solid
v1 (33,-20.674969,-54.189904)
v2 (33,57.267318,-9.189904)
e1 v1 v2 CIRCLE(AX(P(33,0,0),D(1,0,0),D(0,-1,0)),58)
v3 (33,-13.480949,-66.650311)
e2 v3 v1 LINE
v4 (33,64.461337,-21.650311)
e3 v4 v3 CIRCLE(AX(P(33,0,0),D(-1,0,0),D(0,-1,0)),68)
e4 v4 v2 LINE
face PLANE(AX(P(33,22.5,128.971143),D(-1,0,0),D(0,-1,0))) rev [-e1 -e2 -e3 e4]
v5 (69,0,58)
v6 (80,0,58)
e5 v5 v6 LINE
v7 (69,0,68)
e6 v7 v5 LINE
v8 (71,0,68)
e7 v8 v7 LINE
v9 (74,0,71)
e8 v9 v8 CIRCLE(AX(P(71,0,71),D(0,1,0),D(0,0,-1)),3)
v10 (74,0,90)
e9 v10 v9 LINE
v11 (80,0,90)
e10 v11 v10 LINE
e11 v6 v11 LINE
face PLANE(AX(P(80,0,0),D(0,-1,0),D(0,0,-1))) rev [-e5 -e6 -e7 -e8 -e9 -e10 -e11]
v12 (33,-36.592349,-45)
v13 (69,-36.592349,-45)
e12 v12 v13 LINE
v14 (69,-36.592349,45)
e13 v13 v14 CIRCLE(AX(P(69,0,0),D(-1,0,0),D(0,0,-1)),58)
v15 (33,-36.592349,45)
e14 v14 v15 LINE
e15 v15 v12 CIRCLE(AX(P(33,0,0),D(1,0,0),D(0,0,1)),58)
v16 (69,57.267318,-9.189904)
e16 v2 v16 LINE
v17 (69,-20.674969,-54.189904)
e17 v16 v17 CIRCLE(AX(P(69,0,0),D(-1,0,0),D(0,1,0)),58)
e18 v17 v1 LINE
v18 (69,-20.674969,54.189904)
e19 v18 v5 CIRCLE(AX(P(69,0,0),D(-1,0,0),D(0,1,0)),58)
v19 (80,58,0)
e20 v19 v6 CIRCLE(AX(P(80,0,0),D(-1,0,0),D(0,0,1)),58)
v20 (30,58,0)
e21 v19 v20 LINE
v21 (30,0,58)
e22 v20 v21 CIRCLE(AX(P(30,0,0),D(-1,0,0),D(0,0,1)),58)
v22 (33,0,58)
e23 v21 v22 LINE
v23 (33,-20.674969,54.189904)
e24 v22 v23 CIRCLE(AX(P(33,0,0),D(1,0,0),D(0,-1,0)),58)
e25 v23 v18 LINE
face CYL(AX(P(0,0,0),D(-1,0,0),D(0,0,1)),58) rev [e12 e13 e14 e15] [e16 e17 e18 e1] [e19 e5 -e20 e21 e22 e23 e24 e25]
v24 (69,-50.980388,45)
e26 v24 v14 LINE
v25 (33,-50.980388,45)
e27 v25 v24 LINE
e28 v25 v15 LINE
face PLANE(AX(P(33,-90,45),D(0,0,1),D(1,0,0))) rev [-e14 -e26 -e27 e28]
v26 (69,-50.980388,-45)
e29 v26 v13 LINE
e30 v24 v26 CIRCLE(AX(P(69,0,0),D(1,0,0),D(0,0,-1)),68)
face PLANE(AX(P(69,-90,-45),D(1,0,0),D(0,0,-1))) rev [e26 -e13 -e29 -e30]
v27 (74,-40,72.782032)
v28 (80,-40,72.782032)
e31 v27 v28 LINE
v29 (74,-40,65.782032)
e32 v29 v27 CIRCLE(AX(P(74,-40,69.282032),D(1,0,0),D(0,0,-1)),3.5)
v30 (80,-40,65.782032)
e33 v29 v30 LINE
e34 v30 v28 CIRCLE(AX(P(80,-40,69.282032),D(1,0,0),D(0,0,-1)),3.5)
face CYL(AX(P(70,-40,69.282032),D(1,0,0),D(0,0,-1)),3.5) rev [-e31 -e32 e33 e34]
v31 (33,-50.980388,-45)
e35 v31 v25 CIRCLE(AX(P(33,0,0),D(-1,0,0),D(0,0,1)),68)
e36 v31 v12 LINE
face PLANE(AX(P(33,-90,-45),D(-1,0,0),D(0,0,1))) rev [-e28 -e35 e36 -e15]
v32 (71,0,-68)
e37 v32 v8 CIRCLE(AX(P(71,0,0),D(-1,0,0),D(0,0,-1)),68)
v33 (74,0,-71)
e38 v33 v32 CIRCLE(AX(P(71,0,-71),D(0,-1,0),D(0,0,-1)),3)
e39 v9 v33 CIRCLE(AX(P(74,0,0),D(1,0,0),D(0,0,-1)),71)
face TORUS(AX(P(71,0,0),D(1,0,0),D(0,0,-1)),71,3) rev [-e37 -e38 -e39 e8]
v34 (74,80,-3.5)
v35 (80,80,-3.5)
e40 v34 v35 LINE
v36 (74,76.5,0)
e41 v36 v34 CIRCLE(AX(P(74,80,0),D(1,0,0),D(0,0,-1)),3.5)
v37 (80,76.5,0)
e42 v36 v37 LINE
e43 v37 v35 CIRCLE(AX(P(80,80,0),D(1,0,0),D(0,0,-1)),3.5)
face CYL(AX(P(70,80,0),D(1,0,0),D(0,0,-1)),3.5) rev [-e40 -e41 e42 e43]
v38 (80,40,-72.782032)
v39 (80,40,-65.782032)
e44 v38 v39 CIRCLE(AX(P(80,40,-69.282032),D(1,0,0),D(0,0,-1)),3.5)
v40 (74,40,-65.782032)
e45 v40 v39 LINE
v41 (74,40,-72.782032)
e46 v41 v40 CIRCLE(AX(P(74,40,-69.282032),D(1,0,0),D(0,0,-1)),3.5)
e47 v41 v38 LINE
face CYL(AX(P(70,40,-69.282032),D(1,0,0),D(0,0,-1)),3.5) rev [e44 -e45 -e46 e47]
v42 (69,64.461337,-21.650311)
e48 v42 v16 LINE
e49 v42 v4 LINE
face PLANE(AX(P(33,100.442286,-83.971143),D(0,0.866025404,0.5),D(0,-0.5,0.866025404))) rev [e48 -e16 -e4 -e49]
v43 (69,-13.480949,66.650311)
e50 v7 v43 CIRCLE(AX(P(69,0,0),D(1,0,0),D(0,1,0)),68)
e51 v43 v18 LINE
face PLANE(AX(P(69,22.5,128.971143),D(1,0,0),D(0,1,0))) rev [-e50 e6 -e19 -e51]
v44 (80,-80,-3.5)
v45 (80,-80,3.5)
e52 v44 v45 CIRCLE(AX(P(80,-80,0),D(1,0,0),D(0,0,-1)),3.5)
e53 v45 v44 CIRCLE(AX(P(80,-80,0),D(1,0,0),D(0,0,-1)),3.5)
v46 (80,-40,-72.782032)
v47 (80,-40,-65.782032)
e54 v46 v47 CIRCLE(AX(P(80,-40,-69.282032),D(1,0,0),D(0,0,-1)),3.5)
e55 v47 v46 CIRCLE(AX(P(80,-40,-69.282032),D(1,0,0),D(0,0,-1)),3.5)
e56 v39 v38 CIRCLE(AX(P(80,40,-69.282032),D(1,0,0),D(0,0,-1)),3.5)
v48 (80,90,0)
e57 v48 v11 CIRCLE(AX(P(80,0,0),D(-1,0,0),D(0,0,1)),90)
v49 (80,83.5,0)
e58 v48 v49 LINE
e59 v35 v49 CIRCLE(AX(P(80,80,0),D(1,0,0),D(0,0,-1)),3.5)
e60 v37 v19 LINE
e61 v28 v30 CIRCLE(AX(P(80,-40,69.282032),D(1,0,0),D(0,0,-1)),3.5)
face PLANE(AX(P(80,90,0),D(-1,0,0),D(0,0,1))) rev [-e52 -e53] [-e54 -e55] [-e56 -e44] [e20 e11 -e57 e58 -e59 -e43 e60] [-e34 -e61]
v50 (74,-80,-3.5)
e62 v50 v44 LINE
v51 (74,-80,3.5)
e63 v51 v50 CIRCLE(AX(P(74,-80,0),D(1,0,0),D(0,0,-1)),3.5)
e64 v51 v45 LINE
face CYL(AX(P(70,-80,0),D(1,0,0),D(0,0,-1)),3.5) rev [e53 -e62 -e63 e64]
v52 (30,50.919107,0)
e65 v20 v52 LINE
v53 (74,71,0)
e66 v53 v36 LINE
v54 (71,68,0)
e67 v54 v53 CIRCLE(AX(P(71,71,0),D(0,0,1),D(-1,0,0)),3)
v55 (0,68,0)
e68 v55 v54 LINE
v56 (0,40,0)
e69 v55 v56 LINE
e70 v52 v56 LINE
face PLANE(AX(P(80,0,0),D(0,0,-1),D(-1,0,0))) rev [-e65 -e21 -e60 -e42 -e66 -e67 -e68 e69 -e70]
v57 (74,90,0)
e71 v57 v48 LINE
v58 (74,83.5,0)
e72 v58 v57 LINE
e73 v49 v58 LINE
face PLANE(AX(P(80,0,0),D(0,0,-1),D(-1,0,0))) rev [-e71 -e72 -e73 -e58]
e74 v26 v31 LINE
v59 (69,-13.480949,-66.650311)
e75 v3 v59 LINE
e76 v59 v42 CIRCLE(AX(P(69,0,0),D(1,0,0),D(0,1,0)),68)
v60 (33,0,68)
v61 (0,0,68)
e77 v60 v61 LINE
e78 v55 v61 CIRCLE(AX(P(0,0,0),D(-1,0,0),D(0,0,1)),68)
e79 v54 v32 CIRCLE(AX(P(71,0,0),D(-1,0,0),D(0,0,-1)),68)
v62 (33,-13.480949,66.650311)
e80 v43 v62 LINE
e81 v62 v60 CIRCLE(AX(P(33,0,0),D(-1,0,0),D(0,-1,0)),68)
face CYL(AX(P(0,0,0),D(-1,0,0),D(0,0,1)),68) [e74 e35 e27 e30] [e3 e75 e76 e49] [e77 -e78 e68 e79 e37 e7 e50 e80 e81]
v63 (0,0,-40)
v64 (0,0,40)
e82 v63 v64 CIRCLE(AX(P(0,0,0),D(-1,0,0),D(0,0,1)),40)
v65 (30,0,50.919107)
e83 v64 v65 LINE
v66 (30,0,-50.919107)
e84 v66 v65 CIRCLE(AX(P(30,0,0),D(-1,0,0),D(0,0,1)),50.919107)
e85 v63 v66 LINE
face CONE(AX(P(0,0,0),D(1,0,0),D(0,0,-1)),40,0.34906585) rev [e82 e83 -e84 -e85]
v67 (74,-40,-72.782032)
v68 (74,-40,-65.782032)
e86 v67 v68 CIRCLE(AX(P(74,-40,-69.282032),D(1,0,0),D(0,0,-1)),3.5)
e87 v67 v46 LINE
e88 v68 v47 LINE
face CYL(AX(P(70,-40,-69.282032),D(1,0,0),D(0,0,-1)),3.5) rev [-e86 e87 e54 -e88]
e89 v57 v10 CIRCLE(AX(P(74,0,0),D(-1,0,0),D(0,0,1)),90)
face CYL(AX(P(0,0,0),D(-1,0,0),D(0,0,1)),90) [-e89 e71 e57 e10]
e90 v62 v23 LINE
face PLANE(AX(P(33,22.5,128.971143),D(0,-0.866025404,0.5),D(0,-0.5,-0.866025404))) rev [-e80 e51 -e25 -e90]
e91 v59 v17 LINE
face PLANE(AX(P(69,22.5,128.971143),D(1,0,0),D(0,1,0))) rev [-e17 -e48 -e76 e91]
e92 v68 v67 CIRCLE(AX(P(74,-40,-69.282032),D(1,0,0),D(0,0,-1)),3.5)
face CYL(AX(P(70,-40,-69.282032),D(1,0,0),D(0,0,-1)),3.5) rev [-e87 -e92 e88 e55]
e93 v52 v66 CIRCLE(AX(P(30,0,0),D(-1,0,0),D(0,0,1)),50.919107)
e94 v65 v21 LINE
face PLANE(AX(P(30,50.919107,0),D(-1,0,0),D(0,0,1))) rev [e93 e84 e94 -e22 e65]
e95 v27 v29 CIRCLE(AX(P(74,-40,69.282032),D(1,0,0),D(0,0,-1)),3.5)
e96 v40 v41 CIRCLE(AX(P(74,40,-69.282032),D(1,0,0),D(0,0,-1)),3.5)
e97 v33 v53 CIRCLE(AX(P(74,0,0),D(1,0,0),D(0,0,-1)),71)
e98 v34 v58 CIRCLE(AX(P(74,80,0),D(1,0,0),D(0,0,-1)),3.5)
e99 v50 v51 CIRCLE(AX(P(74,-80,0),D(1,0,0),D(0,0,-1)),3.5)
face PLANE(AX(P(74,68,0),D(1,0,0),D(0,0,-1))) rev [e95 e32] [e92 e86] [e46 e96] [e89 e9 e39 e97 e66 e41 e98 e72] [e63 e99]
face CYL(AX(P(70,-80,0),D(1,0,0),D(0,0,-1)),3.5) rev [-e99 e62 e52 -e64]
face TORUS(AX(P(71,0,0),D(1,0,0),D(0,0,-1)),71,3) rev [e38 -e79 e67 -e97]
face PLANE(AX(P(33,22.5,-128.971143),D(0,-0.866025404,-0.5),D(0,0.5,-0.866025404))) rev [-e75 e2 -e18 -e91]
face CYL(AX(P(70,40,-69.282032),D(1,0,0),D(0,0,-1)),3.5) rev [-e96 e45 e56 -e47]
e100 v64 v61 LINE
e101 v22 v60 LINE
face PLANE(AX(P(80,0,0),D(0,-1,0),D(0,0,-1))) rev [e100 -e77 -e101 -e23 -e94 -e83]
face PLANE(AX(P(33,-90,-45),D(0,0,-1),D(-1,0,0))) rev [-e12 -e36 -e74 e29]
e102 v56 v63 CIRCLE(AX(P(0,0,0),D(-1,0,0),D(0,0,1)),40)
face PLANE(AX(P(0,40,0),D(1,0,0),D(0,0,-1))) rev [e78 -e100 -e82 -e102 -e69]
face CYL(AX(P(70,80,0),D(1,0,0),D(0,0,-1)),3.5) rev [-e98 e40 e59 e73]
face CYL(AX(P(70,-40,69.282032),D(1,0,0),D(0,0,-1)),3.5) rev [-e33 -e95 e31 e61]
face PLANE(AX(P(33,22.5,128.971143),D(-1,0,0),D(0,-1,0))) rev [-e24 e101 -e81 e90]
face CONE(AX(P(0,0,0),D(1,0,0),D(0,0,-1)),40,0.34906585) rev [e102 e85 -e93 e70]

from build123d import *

# Parameters (mm, degrees)
SKETCH2_R          = 3.5
CUT_EXTRUDE1_DEPTH = 10
FILLET1_R          = 3
SKETCH3_W          = 36
SKETCH3_H          = 90
CUT_EXTRUDE2_DEPTH = 151.332963784
CIRPATTERN1_COUNT  = 3
SKETCH4_W          = 114.578796514
SKETCH4_H          = 147.158368746
CUT_EXTRUDE3_DEPTH = 151.332963784


with BuildPart() as part:
    # Sketch1 → Revolve1 (revolve)
    with BuildSketch(Plane.XY, mode=Mode.PRIVATE) as revolve1_sk:
        Polygon((0, 40), (0, 68), (74, 68), (74, 90), (80, 90), (80, 58), (30, 58), (30, 50.919107028), align=None)
    revolve(revolve1_sk.sketch.rotate(Axis((0, 0, 0), (1, 0, 0)), 90), axis=Axis((0, 0, 0), (1, 0, 0)))

    # Sketch2 → Cut-Extrude1 (cut)
    with BuildSketch(Plane(origin=(80, 0, 0), x_dir=(0, 0, -1), z_dir=(1, 0, 0))):
        with Locations((0, 80)):
            Circle(SKETCH2_R)
        with Locations((69.282032303, 40)):
            Circle(SKETCH2_R)
        with Locations((69.282032303, -40)):
            Circle(SKETCH2_R)
        with Locations((0, -80)):
            Circle(SKETCH2_R)
        with Locations((-69.282032303, -40)):
            Circle(SKETCH2_R)
        with Locations((-69.282032303, 40)):
            Circle(SKETCH2_R)
    extrude(amount=-CUT_EXTRUDE1_DEPTH, mode=Mode.SUBTRACT)

    # Fillet1
    fillet1_edges = [part.edges().sort_by_distance(p)[0] for p in [
        (74, 0, -68),
    ]]
    fillet(fillet1_edges, radius=FILLET1_R)

    # Sketch3 → Cut-Extrude2 (cut, through all)
    with BuildSketch(Plane(origin=(0, 0, 0), x_dir=(1, 0, 0), z_dir=(0, 1, 0))):
        with Locations((51, 0)):
            Rectangle(SKETCH3_W, SKETCH3_H)
    cut_extrude2 = extrude(amount=-CUT_EXTRUDE2_DEPTH, mode=Mode.SUBTRACT)

    # CirPattern1: Cut-Extrude2 ×3 about axis
    cirpattern1_axis = Axis((0, 0, 0), (1, 0, 0))
    for i in range(1, CIRPATTERN1_COUNT):
        add(cut_extrude2.rotate(cirpattern1_axis, i * 360 / CIRPATTERN1_COUNT), mode=Mode.SUBTRACT)

    # Sketch4 → Cut-Extrude3 (cut, through all)
    with BuildSketch(Plane.ZY):
        with Locations((57.289398257, 73.579184373)):
            Rectangle(SKETCH4_W, SKETCH4_H)
    extrude(amount=-CUT_EXTRUDE3_DEPTH, mode=Mode.SUBTRACT)


solid = part.part
